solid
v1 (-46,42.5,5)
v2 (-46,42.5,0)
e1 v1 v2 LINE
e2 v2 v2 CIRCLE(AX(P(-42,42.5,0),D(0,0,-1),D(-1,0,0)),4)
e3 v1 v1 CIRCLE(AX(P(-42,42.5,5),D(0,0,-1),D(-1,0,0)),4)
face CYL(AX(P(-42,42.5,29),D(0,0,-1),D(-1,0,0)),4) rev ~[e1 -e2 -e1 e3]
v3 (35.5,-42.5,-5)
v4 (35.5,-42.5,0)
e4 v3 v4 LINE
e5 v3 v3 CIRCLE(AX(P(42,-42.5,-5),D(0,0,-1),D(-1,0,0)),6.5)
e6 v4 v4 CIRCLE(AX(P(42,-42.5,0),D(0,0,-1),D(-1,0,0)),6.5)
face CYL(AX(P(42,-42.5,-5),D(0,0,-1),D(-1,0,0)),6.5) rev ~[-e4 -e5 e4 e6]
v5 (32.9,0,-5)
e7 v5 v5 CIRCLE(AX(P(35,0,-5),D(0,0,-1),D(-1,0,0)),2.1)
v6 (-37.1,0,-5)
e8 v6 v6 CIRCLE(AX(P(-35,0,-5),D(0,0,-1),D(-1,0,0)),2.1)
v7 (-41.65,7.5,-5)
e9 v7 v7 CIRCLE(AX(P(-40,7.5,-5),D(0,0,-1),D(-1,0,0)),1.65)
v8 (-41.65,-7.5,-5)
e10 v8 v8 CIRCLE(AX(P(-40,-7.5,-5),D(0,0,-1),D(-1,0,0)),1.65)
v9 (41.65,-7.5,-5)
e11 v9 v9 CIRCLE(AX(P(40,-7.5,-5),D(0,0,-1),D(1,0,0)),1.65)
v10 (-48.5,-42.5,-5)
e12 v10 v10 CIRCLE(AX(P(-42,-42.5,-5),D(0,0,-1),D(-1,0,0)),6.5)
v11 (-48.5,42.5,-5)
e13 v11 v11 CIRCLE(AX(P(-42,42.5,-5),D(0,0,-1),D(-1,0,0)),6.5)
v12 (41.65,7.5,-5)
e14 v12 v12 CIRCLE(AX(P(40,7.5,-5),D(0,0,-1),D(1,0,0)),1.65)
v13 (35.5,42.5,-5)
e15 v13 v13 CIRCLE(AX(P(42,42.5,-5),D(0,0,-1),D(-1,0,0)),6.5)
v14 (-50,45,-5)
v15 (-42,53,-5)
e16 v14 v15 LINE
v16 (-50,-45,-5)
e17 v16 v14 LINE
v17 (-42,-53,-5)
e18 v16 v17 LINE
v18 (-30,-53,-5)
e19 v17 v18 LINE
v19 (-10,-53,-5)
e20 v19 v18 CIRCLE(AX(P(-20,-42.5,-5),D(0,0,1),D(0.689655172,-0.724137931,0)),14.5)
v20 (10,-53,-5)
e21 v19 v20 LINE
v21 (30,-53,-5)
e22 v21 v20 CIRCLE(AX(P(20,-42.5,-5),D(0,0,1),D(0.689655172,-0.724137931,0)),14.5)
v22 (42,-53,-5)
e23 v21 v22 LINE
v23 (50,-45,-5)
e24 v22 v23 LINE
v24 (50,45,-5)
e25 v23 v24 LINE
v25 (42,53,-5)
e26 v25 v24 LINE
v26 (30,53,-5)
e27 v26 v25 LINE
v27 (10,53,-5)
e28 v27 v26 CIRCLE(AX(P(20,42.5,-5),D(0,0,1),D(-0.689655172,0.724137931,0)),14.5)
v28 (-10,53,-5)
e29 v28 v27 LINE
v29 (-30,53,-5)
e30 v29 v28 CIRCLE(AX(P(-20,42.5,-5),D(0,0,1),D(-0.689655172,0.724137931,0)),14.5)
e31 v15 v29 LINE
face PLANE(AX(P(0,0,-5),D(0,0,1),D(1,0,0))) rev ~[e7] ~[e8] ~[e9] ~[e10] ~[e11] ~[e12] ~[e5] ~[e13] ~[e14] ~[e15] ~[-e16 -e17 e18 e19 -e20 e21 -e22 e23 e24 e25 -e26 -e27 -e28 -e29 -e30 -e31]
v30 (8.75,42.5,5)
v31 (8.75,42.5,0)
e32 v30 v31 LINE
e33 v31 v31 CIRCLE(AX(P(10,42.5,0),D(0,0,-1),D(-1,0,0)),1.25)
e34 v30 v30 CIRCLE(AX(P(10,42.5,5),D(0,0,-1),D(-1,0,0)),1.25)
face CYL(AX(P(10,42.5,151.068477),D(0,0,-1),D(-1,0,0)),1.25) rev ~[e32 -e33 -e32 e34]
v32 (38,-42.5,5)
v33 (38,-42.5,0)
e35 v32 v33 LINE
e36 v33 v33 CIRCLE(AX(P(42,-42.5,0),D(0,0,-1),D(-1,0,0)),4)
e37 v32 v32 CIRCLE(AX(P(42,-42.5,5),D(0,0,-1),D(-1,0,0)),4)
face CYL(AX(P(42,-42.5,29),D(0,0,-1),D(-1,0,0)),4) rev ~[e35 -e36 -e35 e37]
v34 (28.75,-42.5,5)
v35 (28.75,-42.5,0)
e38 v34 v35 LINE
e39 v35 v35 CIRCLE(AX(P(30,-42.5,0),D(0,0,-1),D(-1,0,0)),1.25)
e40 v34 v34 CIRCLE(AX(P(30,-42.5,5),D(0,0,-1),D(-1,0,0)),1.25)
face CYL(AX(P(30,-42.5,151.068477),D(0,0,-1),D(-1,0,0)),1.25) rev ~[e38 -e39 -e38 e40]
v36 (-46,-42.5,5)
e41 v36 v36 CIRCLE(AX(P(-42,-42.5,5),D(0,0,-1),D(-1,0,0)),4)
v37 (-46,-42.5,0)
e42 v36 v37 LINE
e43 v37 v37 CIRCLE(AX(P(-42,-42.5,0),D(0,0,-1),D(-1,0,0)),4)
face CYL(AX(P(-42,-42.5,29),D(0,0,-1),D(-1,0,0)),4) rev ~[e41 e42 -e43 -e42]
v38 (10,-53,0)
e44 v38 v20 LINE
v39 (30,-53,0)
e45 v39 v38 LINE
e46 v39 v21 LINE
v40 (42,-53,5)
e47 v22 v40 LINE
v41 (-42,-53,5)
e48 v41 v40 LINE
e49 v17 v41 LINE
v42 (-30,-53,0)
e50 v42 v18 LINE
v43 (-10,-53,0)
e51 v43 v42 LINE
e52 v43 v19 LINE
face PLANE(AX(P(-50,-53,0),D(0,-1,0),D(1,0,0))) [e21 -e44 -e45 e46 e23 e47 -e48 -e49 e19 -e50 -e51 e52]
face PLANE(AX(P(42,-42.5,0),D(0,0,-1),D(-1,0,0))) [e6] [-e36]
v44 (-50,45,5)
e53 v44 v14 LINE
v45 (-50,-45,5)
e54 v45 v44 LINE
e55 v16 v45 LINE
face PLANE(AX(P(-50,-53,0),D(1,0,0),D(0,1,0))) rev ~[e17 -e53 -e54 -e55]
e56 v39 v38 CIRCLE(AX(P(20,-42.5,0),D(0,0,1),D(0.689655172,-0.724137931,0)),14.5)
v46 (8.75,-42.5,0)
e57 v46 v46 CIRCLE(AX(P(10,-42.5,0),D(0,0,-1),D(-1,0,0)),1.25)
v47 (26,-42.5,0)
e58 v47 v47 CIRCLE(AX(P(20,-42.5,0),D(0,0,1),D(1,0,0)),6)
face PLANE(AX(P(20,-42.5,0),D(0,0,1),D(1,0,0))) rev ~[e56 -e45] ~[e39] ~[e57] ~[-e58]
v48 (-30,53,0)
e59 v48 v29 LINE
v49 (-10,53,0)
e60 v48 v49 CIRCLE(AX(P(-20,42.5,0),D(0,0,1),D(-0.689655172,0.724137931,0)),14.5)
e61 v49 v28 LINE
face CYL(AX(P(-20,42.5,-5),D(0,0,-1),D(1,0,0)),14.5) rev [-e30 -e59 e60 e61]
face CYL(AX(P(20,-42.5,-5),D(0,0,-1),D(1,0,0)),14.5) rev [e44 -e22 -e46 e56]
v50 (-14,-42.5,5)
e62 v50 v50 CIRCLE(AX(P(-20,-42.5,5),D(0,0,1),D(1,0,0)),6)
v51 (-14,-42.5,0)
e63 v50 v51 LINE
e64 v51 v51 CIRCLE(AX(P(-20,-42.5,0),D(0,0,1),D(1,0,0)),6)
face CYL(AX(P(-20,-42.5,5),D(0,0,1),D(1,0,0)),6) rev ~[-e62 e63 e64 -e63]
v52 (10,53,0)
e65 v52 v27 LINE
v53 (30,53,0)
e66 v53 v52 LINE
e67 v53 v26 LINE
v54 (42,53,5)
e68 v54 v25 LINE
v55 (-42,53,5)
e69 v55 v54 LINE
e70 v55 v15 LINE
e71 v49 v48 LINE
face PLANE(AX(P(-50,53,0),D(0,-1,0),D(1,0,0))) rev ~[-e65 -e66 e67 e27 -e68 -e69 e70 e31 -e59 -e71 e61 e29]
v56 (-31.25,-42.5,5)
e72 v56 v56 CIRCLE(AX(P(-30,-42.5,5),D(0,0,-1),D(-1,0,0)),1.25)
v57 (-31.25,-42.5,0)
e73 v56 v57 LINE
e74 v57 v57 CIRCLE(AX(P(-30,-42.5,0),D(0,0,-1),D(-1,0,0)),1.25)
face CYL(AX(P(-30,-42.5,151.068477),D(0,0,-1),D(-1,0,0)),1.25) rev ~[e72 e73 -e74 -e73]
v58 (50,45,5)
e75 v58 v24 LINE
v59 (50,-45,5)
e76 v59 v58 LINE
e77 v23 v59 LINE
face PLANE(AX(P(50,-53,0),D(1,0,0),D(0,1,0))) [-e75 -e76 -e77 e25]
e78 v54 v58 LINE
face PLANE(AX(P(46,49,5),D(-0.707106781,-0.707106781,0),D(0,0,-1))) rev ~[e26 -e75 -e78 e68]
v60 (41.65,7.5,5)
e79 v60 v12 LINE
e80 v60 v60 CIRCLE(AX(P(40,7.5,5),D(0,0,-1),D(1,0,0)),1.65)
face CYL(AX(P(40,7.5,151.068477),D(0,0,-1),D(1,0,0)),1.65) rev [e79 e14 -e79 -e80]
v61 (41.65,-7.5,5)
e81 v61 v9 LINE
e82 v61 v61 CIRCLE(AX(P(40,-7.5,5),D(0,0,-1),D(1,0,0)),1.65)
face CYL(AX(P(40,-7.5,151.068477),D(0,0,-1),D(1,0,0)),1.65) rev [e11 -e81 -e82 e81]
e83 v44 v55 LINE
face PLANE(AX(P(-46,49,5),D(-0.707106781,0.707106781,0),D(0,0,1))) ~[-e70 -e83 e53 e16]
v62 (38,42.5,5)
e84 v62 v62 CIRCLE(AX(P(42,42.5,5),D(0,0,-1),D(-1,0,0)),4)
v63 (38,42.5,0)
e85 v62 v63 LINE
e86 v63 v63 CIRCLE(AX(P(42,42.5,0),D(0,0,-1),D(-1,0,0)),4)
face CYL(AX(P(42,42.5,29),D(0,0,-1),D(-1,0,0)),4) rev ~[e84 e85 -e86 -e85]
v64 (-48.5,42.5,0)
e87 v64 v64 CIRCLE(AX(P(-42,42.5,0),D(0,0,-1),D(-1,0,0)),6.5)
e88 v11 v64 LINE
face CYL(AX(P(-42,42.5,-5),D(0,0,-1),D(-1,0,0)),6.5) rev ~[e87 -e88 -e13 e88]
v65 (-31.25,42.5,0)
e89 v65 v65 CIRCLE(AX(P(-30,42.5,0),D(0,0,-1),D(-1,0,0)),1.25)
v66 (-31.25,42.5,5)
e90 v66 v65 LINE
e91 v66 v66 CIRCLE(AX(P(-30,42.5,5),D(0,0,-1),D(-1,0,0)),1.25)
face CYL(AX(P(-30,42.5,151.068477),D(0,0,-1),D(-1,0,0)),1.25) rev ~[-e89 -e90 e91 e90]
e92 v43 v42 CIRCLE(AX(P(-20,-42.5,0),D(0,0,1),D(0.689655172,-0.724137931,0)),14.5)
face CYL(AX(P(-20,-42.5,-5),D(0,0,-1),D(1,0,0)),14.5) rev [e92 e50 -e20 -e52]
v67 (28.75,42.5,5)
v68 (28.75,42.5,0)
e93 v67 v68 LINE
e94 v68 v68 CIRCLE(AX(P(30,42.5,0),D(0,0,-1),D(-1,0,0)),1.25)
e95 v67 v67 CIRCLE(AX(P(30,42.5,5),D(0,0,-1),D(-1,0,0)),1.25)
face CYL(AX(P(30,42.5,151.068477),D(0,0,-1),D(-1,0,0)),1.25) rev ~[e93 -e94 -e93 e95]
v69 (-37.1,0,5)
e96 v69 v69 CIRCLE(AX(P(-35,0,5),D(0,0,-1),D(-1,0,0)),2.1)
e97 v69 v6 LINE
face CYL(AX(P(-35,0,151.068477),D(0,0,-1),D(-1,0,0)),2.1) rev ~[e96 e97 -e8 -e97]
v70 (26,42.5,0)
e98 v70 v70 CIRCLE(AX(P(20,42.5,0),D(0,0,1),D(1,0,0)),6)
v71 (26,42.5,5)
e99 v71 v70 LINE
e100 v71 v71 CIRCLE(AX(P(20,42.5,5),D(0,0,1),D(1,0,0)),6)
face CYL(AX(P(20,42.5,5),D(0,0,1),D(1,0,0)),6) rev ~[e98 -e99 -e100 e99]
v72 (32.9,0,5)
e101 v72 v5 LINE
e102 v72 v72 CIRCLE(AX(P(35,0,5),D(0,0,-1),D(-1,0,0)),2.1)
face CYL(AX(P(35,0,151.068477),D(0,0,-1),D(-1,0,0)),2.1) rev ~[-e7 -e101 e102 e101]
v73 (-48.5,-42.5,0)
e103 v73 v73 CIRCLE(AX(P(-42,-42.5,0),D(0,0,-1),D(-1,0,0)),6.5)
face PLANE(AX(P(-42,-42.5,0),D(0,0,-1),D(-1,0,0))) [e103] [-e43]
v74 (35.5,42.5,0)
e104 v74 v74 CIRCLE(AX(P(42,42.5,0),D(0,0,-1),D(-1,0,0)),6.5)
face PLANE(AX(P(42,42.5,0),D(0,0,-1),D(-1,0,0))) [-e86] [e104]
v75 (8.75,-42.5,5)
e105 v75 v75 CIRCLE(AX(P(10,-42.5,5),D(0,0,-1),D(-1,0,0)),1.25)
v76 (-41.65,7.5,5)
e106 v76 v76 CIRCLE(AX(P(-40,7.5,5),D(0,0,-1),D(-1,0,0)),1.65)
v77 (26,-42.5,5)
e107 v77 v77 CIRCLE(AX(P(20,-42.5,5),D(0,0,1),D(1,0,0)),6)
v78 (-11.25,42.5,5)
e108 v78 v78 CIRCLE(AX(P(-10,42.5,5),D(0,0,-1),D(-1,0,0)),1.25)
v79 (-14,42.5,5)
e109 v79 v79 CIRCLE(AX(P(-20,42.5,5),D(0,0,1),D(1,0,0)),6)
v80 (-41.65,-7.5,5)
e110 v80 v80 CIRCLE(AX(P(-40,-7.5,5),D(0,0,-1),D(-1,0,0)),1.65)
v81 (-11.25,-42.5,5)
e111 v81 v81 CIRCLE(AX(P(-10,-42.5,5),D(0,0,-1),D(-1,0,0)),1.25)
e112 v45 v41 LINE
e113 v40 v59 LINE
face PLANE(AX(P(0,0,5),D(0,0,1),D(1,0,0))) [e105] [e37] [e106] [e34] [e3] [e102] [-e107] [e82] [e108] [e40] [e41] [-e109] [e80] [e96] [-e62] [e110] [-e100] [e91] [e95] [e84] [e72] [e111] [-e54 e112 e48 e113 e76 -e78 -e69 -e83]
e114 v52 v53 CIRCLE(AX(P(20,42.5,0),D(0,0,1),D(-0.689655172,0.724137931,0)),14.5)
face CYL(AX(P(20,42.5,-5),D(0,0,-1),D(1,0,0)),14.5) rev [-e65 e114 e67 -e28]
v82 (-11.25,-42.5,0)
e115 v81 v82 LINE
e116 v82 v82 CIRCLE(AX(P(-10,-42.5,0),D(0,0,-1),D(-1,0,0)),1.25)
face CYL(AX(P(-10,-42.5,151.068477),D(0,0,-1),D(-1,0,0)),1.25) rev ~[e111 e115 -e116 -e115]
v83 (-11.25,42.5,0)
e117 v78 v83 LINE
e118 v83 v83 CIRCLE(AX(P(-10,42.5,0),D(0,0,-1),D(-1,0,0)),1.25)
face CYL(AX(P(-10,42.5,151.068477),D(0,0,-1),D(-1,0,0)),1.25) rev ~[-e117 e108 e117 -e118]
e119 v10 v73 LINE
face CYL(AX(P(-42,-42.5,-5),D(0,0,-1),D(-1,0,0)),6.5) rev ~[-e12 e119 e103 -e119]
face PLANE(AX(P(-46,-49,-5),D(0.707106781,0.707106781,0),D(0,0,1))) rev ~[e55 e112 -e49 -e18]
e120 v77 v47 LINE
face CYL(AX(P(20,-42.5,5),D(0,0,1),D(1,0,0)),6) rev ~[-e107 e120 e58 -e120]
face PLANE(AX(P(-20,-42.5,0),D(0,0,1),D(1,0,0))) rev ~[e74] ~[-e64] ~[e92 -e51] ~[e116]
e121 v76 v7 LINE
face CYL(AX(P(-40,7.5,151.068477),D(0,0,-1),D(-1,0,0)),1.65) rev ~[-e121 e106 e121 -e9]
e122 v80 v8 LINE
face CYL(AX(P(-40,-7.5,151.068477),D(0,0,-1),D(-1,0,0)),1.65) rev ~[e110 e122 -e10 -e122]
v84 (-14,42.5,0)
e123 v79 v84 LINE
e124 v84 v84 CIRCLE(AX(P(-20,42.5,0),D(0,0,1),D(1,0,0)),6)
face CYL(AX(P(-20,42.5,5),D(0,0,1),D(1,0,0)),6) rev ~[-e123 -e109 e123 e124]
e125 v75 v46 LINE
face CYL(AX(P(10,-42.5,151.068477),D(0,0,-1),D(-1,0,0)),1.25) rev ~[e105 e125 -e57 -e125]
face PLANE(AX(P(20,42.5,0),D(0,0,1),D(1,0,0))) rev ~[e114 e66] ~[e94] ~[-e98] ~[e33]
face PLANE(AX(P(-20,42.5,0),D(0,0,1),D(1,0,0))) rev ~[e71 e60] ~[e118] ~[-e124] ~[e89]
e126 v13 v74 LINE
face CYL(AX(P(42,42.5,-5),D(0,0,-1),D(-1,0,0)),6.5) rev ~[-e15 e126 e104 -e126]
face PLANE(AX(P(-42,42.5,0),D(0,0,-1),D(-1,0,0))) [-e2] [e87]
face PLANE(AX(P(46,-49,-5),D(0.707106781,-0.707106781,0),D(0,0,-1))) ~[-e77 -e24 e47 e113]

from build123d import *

# Parameters (mm, degrees)
SKETCH_1_W                   = 100
SKETCH_1_H                   = 106
EXTRUDE_1_DEPTH              = 5
HOLE_WIZARD_M5_1_D           = 4.2
CHAMFER_1_SIZE               = 8
HOLE_WIZARD_M4_1_D           = 3.3
SKETCH_10_R                  = 6
EXTRUDE1_DEPTH               = 74.545904033
M3_TAPPED_HOLE1_D            = 2.5
SKETCH3_R                    = 14.5
EXTRUDE2_DEPTH               = 5
F_8_0_8_DIAMETER_HOLE1_D     = 8
F_8_0_8_DIAMETER_HOLE1_DEPTH = 24
F_8_0_8_DIAMETER_HOLE1_TIP   = 2.403442476
SKETCH6_R                    = 6.5
EXTRUDE3_DEPTH               = 5


with BuildPart() as part:
    # 草图1 → 凸台-拉伸1 (new, symmetric)
    with BuildSketch(Plane.XY):
        Rectangle(SKETCH_1_W, SKETCH_1_H)
    extrude(amount=EXTRUDE_1_DEPTH, both=True)

    # M5 螺纹孔1 (through all)
    with Locations(Plane.XY.offset(5)):
        with Locations((-35, 0), (35, 0)):
            Hole(HOLE_WIZARD_M5_1_D / 2)

    # 倒角1
    chamfer_1_edges = [part.edges().sort_by_distance(p)[0] for p in [
        (50, -53, 0),
        (-50, -53, 0),
        (-50, 53, 0),
        (50, 53, 0),
    ]]
    chamfer(chamfer_1_edges, length=CHAMFER_1_SIZE)

    # M4 螺纹孔1 (through all)
    with Locations(Plane.XY.offset(5)):
        with Locations((-40, -7.5), (-40, 7.5)):
            hole_wizard_m4_1 = Hole(HOLE_WIZARD_M4_1_D / 2)

    # 镜向2: M4 螺纹孔1 across plane
    add(hole_wizard_m4_1.mirror(Plane(origin=(0, 0, 0), x_dir=(0, 0, 1), z_dir=(1, 0, 0))), mode=Mode.SUBTRACT)

    # 草图10 → Extrude1 (cut, through all)
    with BuildSketch(Plane.XY.offset(5)):
        with Locations((-20, 42.5)):
            Circle(SKETCH_10_R)
        with Locations((-20, -42.5)):
            Circle(SKETCH_10_R)
        with Locations((20, -42.5)):
            Circle(SKETCH_10_R)
        with Locations((20, 42.5)):
            Circle(SKETCH_10_R)
    extrude(amount=-EXTRUDE1_DEPTH, mode=Mode.SUBTRACT)

    # M3 Tapped Hole1 (through all)
    with Locations(Plane.XY.offset(5)):
        with Locations((10, -42.5), (30, -42.5), (-10, -42.5), (-30, -42.5), (-10, 42.5), (-30, 42.5), (10, 42.5), (30, 42.5)):
            Hole(M3_TAPPED_HOLE1_D / 2)

    # Sketch3 → Extrude2 (cut)
    with BuildSketch(Plane.XY.offset(-5)):
        with Locations((-20, 42.5)):
            Circle(SKETCH3_R)
        with Locations((-20, -42.5)):
            Circle(SKETCH3_R)
        with Locations((20, -42.5)):
            Circle(SKETCH3_R)
        with Locations((20, 42.5)):
            Circle(SKETCH3_R)
    extrude(amount=EXTRUDE2_DEPTH, mode=Mode.SUBTRACT)

    # Ø8.0 (8) Diameter Hole1
    with Locations(Plane.XY.offset(5)):
        with Locations((-42, 42.5), (42, 42.5), (42, -42.5), (-42, -42.5)):
            Hole(F_8_0_8_DIAMETER_HOLE1_D / 2, depth=F_8_0_8_DIAMETER_HOLE1_DEPTH)
            with Locations((0, 0, -(F_8_0_8_DIAMETER_HOLE1_DEPTH + F_8_0_8_DIAMETER_HOLE1_TIP / 2))):  # 118° drill point
                Cone(0, F_8_0_8_DIAMETER_HOLE1_D / 2, F_8_0_8_DIAMETER_HOLE1_TIP, mode=Mode.SUBTRACT)

    # Sketch6 → Extrude3 (cut)
    with BuildSketch(Plane(origin=(0, 0, -5), x_dir=(-1, 0, 0), z_dir=(0, 0, -1))):
        with Locations((42, -42.5)):
            Circle(SKETCH6_R)
        with Locations((-42, -42.5)):
            Circle(SKETCH6_R)
        with Locations((42, 42.5)):
            Circle(SKETCH6_R)
        with Locations((-42, 42.5)):
            Circle(SKETCH6_R)
    extrude(amount=-EXTRUDE3_DEPTH, mode=Mode.SUBTRACT)


solid = part.part
